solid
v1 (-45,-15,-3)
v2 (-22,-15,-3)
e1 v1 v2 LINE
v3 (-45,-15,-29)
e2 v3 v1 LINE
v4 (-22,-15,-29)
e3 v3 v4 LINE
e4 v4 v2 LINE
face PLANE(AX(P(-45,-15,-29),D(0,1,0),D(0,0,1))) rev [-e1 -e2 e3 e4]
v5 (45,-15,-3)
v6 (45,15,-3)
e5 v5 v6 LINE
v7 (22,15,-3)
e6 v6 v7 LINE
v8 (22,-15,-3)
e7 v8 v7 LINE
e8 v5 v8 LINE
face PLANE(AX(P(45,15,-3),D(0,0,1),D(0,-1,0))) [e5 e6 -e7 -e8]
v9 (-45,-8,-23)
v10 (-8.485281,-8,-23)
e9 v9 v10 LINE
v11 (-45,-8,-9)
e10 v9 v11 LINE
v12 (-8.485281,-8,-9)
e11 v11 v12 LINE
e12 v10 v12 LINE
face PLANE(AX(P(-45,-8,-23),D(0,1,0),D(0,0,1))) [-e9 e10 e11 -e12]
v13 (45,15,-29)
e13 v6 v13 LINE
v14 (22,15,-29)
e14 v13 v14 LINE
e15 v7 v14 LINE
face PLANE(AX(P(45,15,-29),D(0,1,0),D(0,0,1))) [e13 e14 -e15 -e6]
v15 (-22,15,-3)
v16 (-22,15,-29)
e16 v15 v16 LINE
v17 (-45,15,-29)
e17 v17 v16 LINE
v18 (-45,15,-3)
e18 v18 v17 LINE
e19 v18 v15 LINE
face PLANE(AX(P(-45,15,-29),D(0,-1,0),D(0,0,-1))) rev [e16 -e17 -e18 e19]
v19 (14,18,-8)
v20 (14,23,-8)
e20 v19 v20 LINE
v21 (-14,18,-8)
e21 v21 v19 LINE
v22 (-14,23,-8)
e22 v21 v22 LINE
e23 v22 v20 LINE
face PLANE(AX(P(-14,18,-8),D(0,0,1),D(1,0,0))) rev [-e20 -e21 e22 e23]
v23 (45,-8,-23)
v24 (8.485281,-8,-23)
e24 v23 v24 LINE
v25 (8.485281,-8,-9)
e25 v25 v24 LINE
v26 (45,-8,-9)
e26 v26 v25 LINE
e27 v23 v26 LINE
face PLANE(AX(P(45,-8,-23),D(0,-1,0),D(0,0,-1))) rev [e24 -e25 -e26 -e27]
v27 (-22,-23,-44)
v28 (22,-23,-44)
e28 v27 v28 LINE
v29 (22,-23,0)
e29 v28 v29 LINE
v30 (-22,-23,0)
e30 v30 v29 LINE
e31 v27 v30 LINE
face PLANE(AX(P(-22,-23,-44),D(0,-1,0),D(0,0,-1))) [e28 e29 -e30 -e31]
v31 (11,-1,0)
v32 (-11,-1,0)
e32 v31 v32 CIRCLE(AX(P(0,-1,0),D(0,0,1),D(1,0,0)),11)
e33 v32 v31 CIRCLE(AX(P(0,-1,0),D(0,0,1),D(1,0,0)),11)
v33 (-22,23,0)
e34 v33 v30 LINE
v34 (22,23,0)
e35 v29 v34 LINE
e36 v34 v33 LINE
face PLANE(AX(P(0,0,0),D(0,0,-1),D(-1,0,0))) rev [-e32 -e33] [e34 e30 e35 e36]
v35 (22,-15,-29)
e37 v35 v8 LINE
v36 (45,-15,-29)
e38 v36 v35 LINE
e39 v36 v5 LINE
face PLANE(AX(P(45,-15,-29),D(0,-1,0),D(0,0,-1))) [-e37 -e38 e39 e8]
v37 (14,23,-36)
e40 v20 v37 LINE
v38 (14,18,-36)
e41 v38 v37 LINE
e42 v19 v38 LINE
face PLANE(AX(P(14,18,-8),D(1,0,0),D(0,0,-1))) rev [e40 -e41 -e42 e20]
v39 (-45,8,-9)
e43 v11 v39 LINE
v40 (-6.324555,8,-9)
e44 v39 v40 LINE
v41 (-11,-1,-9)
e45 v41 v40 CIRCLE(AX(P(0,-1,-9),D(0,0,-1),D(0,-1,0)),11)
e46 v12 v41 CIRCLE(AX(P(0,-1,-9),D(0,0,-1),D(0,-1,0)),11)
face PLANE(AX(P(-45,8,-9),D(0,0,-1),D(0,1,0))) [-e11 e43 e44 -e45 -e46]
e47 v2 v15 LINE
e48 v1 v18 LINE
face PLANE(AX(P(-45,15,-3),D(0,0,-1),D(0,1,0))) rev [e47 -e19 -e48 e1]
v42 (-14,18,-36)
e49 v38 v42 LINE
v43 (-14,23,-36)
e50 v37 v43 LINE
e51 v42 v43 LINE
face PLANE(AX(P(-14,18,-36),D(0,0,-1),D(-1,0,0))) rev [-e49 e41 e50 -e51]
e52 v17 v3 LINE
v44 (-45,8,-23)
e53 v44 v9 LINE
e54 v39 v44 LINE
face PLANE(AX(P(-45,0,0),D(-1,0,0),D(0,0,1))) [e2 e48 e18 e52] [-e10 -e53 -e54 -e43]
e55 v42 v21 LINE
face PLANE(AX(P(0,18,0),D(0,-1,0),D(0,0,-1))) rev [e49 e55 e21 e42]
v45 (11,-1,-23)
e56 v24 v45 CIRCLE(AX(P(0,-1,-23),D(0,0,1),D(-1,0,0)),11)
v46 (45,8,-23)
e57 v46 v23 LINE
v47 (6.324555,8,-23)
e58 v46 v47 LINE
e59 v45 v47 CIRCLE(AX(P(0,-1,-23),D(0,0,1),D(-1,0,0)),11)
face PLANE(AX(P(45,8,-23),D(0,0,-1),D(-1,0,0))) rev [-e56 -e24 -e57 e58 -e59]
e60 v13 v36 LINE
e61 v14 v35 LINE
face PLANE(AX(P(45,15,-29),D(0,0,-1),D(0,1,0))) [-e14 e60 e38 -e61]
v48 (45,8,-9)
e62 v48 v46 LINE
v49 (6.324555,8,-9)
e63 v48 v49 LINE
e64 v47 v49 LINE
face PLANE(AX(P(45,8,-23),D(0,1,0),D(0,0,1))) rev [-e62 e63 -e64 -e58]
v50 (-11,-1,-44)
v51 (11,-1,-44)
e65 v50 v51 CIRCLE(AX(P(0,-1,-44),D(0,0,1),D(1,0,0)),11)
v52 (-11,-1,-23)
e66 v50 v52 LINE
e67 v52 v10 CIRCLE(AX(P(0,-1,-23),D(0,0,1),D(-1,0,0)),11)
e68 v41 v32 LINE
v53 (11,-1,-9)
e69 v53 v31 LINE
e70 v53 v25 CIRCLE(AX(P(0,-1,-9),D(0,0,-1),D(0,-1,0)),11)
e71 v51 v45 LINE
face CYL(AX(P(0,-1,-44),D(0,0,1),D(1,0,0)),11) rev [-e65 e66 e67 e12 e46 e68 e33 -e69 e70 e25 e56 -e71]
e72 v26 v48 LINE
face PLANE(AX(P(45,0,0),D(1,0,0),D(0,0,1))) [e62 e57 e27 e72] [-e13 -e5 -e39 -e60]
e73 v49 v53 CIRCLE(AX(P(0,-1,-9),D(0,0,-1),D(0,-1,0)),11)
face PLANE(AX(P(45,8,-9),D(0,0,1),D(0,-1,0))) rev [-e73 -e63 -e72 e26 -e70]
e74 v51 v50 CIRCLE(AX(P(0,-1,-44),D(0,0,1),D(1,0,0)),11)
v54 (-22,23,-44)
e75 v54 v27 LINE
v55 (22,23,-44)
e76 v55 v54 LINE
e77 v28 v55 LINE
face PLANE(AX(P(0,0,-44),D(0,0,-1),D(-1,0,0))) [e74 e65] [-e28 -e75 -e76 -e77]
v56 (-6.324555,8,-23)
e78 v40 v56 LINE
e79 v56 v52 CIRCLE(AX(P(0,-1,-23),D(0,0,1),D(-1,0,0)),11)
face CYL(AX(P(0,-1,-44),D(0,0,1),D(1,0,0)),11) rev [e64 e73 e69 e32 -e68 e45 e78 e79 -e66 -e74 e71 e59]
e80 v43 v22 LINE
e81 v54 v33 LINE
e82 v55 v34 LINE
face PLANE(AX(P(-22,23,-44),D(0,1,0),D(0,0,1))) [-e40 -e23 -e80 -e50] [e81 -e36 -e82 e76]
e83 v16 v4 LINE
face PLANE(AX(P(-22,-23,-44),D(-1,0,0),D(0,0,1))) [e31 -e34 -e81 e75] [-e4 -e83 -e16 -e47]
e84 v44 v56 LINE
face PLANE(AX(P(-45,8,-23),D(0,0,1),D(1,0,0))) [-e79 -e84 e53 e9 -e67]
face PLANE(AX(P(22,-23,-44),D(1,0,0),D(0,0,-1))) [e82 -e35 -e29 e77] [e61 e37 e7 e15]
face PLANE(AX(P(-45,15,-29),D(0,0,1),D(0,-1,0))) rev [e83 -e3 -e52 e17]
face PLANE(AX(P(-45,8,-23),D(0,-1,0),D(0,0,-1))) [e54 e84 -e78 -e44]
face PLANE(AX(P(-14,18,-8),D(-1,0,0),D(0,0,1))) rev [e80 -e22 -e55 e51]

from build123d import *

# Parameters (mm, degrees)
MAIN_BLOCK_PROFILE_W            = 44
MAIN_BLOCK_PROFILE_H            = 46
MAIN_BLOCK_PROFILE_R            = 11
MAIN_BLOCK_44MM_DEPTH           = 44
TOP_POCKET_PROFILE_28X28_W      = 28
TOP_POCKET_PROFILE_28X28_H      = 28
TOP_SQUARE_POCKET_28X28X5_DEPTH = 5
SIDE_BOSS_PROFILE_W             = 26
SIDE_BOSS_PROFILE_H             = 30
SIDE_BOSS_PROFILE_W_2           = 14
SIDE_BOSS_PROFILE_H_2           = 16
SIDE_SQUARE_BOSS_23MM_DEPTH     = 23
SIDE_OPENING_PROFILE_W          = 14
SIDE_OPENING_PROFILE_H          = 16
SIDE_OPENING_CUT_DEPTH          = 103.786185842


with BuildPart() as part:
    # Main Block Profile → Main Block 44mm (new body)
    with BuildSketch(Plane.XY):
        Rectangle(MAIN_BLOCK_PROFILE_W, MAIN_BLOCK_PROFILE_H)
        with Locations((0, -1)):
            Circle(MAIN_BLOCK_PROFILE_R, mode=Mode.SUBTRACT)
    extrude(amount=-MAIN_BLOCK_44MM_DEPTH)

    # Top Pocket Profile 28x28 → Top Square Pocket 28x28x5 (cut)
    with BuildSketch(Plane(origin=(0, 23, 0), x_dir=(1, 0, 0), z_dir=(0, 1, 0))):
        with Locations((0, 22)):
            Rectangle(TOP_POCKET_PROFILE_28X28_W, TOP_POCKET_PROFILE_28X28_H)
    extrude(amount=-TOP_SQUARE_POCKET_28X28X5_DEPTH, mode=Mode.SUBTRACT)

    # Side Boss Profile → Side Square Boss 23mm (add)
    with BuildSketch(Plane.ZY.offset(22)):
        with Locations((-16, 0)):
            Rectangle(SIDE_BOSS_PROFILE_W, SIDE_BOSS_PROFILE_H)
        with Locations((-16, 0)):
            Rectangle(SIDE_BOSS_PROFILE_W_2, SIDE_BOSS_PROFILE_H_2, mode=Mode.SUBTRACT)
    side_square_boss_23mm = extrude(amount=SIDE_SQUARE_BOSS_23MM_DEPTH)

    # Side Boss Mirror: Side Square Boss 23mm across plane
    add(side_square_boss_23mm.mirror(Plane(origin=(0, 0, 0), x_dir=(0, 0, 1), z_dir=(1, 0, 0))))

    # Side Opening Profile → Side Opening Cut (cut, through all)
    with BuildSketch(Plane(origin=(45, 0, 0), x_dir=(0, 0, -1), z_dir=(1, 0, 0))):
        with Locations((16, 0)):
            Rectangle(SIDE_OPENING_PROFILE_W, SIDE_OPENING_PROFILE_H)
    extrude(amount=-SIDE_OPENING_CUT_DEPTH, mode=Mode.SUBTRACT)


solid = part.part
